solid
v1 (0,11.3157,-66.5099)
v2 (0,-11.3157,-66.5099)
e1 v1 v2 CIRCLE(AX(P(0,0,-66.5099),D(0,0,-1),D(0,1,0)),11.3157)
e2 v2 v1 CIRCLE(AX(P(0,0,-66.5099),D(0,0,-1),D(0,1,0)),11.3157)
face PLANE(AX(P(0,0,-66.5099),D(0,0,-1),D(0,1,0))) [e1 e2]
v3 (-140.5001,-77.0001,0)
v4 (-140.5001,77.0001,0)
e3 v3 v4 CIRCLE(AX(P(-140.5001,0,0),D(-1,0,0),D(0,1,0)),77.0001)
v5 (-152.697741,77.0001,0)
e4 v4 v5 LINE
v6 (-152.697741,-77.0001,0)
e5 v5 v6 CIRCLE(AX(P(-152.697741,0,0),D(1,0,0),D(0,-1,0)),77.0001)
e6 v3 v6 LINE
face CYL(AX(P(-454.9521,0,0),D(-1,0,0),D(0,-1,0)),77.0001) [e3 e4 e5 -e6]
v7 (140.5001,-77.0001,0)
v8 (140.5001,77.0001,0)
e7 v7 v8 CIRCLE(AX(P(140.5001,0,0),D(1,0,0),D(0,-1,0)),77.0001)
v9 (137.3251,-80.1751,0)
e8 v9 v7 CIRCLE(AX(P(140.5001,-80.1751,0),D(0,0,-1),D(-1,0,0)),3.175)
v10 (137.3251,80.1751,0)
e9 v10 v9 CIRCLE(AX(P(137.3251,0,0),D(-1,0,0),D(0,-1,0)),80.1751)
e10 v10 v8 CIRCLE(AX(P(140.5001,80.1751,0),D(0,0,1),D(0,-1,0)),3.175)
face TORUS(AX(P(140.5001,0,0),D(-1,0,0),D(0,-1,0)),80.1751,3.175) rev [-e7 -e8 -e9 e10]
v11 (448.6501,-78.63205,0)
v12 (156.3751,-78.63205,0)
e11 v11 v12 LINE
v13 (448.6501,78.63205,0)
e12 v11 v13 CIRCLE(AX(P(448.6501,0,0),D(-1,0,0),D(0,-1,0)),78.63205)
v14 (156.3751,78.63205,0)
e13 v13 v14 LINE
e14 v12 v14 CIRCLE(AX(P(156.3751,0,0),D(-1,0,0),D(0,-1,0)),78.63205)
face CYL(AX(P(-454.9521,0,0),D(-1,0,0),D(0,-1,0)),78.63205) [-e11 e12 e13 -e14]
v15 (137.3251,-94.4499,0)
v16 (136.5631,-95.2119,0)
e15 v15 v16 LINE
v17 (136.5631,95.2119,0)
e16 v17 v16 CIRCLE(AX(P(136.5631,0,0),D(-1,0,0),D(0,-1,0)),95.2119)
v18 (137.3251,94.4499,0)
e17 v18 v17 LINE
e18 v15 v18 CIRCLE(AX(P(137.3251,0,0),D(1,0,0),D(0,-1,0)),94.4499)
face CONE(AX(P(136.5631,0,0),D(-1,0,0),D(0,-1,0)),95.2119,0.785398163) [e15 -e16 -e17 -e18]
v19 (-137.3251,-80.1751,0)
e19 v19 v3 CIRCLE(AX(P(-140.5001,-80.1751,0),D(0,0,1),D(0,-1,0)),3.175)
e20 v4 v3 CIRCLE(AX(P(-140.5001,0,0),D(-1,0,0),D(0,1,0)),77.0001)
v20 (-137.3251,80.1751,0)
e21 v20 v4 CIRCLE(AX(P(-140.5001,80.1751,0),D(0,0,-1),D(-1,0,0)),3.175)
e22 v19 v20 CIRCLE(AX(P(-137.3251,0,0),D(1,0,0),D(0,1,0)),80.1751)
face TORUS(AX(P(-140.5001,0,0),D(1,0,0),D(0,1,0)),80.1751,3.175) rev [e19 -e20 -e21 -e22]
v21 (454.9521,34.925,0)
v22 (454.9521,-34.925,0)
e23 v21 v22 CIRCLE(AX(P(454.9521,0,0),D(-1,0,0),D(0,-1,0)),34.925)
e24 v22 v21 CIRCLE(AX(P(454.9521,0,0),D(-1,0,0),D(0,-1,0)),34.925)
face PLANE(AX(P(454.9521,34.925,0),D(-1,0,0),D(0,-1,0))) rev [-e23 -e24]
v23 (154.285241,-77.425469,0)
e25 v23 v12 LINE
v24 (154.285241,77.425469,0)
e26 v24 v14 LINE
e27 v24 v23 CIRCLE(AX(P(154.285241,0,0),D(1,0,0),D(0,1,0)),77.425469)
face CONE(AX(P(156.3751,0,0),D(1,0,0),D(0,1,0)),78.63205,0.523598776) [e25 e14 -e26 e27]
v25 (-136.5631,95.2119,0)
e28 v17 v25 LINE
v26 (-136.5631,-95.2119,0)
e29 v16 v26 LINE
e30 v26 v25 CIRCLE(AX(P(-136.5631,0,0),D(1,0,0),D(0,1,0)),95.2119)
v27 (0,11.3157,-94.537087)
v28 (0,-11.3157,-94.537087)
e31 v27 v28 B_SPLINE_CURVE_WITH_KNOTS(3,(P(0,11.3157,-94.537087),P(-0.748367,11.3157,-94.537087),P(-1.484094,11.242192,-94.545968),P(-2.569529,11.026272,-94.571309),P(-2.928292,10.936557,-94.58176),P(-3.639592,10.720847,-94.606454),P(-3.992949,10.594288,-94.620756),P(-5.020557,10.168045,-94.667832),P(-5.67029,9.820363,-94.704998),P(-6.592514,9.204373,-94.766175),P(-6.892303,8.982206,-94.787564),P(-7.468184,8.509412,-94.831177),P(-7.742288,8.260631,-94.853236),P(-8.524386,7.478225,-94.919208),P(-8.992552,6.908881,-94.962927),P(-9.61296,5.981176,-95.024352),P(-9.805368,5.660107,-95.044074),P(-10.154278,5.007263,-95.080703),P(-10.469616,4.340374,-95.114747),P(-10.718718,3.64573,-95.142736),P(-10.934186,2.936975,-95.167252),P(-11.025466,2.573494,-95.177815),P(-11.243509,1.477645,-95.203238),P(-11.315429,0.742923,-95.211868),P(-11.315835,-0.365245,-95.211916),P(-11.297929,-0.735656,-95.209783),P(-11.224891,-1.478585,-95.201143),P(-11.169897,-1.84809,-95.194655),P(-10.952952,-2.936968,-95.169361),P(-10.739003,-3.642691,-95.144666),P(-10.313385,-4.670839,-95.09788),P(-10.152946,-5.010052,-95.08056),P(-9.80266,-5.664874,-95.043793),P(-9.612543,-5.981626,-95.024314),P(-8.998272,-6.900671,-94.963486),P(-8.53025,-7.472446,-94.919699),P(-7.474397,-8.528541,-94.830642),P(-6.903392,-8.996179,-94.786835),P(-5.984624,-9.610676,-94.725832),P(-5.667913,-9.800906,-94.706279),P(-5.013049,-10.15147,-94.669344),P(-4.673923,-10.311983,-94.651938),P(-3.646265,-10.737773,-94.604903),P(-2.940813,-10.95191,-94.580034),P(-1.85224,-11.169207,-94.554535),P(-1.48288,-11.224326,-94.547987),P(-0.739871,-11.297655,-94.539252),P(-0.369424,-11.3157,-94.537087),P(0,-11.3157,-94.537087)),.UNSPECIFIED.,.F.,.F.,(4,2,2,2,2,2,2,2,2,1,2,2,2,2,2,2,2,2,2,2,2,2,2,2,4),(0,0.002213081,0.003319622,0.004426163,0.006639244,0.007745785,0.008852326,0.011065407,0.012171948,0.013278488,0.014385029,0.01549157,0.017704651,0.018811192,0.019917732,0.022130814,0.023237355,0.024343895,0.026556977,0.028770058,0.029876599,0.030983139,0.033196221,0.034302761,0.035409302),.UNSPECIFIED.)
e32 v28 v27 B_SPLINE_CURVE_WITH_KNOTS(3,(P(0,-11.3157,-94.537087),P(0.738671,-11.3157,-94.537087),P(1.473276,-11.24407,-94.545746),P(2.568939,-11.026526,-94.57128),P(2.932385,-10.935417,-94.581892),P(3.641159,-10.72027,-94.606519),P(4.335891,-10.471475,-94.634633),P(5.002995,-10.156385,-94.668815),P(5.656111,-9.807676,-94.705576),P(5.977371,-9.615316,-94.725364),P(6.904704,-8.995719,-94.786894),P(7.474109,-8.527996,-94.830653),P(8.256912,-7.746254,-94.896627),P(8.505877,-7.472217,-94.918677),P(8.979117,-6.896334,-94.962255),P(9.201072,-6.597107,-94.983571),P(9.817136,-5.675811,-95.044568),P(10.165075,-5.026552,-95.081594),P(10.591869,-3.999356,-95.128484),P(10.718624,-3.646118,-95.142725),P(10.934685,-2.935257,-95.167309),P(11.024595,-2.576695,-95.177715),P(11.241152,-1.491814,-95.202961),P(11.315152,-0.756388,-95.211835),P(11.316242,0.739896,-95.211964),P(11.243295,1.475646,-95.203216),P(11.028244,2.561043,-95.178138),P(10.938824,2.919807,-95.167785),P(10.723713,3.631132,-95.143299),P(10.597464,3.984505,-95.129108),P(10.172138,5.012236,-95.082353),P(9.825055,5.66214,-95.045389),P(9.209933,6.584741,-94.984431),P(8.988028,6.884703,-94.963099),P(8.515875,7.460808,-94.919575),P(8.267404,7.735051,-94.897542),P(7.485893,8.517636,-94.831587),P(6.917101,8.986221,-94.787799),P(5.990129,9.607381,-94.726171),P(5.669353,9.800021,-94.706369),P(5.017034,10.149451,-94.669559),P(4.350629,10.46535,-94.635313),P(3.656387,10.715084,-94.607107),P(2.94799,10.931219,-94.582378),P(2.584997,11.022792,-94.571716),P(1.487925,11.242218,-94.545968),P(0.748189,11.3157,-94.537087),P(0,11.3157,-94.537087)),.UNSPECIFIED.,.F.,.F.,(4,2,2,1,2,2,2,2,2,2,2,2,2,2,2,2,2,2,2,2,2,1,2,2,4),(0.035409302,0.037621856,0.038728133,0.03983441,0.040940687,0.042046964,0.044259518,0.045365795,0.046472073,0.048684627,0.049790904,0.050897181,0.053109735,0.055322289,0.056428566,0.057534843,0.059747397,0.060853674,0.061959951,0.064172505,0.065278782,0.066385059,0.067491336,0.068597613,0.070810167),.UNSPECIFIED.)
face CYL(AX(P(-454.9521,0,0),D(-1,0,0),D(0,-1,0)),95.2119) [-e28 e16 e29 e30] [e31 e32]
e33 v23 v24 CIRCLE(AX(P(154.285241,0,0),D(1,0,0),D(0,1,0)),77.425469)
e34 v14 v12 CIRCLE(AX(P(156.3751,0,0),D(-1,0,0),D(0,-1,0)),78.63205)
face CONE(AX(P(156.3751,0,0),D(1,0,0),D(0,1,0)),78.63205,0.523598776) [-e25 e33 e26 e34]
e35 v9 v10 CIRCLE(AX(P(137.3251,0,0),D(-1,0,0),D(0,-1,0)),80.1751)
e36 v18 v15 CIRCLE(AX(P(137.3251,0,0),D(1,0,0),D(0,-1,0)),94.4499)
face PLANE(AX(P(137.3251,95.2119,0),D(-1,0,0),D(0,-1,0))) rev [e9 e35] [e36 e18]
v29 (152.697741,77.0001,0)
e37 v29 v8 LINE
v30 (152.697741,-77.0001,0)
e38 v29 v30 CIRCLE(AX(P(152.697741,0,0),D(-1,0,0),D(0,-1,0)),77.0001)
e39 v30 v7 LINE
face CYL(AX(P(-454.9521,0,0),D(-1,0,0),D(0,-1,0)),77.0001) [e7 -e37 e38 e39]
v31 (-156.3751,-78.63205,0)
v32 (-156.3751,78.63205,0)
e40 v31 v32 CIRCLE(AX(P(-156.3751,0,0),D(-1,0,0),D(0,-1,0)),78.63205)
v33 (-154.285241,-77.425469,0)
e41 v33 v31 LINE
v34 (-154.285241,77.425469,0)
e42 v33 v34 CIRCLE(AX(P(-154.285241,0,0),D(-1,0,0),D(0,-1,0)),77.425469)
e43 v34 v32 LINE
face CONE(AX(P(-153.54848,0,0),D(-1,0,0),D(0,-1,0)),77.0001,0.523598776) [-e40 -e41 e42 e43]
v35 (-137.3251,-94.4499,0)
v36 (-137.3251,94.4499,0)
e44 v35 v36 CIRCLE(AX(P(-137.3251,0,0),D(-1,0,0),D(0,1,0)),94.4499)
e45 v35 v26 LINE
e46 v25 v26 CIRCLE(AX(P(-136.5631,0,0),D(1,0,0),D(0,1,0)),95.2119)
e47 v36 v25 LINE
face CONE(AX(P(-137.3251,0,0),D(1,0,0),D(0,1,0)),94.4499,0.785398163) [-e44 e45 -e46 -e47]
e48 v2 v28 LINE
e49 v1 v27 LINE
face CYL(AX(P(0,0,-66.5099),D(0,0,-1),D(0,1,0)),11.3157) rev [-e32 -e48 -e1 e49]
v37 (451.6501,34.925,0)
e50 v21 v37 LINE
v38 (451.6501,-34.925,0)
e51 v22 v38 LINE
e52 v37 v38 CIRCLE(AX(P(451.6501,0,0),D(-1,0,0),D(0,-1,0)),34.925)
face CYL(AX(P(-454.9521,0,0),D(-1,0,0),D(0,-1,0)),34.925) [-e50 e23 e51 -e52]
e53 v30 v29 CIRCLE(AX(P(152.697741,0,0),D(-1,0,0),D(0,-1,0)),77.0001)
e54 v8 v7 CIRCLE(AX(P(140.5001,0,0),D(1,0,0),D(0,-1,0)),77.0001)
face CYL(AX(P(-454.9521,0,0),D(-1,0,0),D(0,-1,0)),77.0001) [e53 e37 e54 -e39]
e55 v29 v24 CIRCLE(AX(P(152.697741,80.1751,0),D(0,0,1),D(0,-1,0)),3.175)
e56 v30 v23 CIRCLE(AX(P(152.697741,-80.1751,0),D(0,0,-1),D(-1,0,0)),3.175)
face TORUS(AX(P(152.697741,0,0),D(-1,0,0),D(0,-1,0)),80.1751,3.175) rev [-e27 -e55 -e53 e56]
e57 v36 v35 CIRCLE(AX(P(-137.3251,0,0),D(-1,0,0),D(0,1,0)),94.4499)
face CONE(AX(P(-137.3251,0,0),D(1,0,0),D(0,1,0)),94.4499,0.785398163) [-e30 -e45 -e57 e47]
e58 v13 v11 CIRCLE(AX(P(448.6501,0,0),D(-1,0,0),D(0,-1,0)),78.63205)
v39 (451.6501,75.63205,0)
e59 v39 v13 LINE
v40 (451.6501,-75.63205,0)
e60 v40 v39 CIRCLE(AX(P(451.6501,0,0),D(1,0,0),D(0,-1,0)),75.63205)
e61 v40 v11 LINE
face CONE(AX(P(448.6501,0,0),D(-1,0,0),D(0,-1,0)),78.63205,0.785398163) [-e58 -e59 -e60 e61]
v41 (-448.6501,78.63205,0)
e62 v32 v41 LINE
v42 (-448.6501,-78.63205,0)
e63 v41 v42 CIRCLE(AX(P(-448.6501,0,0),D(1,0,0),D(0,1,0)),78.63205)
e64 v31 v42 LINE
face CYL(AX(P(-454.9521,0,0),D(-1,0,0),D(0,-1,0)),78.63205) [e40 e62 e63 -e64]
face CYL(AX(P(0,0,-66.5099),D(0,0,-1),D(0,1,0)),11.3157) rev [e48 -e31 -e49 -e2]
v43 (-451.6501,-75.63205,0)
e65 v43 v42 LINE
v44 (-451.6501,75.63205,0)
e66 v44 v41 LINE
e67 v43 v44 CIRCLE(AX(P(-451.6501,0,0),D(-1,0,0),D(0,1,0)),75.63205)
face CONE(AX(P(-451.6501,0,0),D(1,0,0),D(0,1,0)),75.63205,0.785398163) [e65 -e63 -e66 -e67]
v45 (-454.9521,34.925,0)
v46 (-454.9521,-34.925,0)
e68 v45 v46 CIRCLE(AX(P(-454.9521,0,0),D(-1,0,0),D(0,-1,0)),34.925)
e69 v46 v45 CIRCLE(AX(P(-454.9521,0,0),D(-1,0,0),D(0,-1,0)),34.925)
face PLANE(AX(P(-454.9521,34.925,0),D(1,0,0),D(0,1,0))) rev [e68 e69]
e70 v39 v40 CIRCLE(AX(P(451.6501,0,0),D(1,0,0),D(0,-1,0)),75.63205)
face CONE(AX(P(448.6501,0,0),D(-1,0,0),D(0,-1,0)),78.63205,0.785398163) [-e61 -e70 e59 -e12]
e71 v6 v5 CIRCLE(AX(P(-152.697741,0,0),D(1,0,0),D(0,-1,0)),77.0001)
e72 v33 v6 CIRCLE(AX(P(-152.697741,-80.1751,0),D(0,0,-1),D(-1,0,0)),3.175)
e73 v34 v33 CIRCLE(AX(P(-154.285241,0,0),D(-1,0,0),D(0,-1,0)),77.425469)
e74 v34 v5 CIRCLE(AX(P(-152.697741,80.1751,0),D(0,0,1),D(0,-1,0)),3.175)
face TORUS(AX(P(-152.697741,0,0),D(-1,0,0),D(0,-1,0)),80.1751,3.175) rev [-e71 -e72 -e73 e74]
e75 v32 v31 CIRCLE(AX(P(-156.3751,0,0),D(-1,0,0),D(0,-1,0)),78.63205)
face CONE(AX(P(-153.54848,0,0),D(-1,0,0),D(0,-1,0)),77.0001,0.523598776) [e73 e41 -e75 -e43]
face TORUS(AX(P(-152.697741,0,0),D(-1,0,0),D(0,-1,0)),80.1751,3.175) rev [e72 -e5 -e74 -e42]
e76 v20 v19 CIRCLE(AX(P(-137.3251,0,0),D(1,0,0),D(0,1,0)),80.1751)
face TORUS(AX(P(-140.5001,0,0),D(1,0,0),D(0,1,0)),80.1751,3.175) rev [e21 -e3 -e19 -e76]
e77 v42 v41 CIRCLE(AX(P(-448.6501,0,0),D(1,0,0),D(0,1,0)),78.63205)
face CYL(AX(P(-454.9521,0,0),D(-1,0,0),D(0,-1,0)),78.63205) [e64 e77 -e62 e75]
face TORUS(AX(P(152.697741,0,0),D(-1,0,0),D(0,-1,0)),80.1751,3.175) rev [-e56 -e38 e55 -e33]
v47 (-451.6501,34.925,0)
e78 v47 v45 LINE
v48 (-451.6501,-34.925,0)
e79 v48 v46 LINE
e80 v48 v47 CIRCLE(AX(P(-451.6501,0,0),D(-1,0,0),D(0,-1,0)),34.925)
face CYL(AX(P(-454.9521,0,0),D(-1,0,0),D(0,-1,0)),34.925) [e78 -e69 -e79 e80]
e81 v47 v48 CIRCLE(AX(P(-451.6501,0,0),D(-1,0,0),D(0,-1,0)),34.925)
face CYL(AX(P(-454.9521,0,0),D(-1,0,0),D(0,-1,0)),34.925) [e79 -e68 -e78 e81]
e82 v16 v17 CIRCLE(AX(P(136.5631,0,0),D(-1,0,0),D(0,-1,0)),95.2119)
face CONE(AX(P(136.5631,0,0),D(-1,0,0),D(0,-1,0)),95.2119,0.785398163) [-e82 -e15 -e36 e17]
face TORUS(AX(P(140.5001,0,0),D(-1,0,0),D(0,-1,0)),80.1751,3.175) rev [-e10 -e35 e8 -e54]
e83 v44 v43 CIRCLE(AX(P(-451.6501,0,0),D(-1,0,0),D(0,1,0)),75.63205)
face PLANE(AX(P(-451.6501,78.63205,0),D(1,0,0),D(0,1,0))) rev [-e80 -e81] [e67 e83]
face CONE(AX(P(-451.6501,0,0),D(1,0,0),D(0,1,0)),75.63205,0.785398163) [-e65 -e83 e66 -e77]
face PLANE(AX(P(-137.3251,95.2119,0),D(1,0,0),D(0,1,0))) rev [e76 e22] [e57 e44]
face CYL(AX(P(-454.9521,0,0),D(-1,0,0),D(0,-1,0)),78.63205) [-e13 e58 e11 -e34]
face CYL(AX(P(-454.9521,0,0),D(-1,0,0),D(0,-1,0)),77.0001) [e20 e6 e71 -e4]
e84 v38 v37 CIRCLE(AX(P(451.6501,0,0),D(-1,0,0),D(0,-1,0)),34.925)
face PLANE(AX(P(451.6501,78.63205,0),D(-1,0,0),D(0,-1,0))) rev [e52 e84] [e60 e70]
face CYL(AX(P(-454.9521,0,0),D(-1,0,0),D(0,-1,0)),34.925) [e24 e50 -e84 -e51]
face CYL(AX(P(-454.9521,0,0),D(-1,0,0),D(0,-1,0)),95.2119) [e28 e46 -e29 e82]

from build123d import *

# Parameters (mm, degrees)
CHAMFER1_SIZE      = 3
CHAMFER2_SIZE      = 0.762
FILLET1_R          = 3.175
SKETCH2_R          = 11.3157
CUT_EXTRUDE1_DEPTH = 28.702


with BuildPart() as part:
    # Sketch1 → Revolve1 (revolve)
    with BuildSketch(Plane.XY, mode=Mode.PRIVATE) as revolve1_sk:
        Polygon((137.3251, 95.2119), (-137.3251, 95.2119), (-137.3251, 77.0001), (-153.548479685, 77.0001), (-156.3751, 78.63205), (-451.6501, 78.63205), (-451.6501, 34.925), (-454.9521, 34.925), (-454.9521, 0), (454.9521, 0), (454.9521, 34.925), (451.6501, 34.925), (451.6501, 78.63205), (156.3751, 78.63205), (153.548479685, 77.0001), (137.3251, 77.0001), align=None)
    revolve(revolve1_sk.sketch.rotate(Axis((-454.9521, 0, 0), (1, 0, 0)), 180), axis=Axis((-454.9521, 0, 0), (1, 0, 0)))

    # Chamfer1
    chamfer1_edges = [part.edges().sort_by_distance(p)[0] for p in [
        (-451.6501, 78.63205, 0),
        (451.6501, 78.63205, 0),
    ]]
    chamfer(chamfer1_edges, length=CHAMFER1_SIZE)

    # Chamfer2
    chamfer2_edges = [part.edges().sort_by_distance(p)[0] for p in [
        (137.3251, 95.2119, 0),
        (-137.3251, 95.2119, 0),
    ]]
    chamfer(chamfer2_edges, length=CHAMFER2_SIZE)

    # Fillet1
    fillet1_edges = [part.edges().sort_by_distance(p)[0] for p in [
        (-137.3251, 77.0001, 0),
        (-153.548479685, 77.0001, 0),
        (153.548479685, 77.0001, 0),
        (137.3251, 77.0001, 0),
    ]]
    fillet(fillet1_edges, radius=FILLET1_R)

    # Sketch2 → Cut-Extrude1 (cut)
    with BuildSketch(Plane(origin=(0, 0, -95.2119), x_dir=(0, -1, 0), z_dir=(0, 0, -1))):
        with Locations(Location((0, 0, 0), (0, 0, 180))):
            Circle(SKETCH2_R)
    extrude(amount=-CUT_EXTRUDE1_DEPTH, mode=Mode.SUBTRACT)


solid = part.part
